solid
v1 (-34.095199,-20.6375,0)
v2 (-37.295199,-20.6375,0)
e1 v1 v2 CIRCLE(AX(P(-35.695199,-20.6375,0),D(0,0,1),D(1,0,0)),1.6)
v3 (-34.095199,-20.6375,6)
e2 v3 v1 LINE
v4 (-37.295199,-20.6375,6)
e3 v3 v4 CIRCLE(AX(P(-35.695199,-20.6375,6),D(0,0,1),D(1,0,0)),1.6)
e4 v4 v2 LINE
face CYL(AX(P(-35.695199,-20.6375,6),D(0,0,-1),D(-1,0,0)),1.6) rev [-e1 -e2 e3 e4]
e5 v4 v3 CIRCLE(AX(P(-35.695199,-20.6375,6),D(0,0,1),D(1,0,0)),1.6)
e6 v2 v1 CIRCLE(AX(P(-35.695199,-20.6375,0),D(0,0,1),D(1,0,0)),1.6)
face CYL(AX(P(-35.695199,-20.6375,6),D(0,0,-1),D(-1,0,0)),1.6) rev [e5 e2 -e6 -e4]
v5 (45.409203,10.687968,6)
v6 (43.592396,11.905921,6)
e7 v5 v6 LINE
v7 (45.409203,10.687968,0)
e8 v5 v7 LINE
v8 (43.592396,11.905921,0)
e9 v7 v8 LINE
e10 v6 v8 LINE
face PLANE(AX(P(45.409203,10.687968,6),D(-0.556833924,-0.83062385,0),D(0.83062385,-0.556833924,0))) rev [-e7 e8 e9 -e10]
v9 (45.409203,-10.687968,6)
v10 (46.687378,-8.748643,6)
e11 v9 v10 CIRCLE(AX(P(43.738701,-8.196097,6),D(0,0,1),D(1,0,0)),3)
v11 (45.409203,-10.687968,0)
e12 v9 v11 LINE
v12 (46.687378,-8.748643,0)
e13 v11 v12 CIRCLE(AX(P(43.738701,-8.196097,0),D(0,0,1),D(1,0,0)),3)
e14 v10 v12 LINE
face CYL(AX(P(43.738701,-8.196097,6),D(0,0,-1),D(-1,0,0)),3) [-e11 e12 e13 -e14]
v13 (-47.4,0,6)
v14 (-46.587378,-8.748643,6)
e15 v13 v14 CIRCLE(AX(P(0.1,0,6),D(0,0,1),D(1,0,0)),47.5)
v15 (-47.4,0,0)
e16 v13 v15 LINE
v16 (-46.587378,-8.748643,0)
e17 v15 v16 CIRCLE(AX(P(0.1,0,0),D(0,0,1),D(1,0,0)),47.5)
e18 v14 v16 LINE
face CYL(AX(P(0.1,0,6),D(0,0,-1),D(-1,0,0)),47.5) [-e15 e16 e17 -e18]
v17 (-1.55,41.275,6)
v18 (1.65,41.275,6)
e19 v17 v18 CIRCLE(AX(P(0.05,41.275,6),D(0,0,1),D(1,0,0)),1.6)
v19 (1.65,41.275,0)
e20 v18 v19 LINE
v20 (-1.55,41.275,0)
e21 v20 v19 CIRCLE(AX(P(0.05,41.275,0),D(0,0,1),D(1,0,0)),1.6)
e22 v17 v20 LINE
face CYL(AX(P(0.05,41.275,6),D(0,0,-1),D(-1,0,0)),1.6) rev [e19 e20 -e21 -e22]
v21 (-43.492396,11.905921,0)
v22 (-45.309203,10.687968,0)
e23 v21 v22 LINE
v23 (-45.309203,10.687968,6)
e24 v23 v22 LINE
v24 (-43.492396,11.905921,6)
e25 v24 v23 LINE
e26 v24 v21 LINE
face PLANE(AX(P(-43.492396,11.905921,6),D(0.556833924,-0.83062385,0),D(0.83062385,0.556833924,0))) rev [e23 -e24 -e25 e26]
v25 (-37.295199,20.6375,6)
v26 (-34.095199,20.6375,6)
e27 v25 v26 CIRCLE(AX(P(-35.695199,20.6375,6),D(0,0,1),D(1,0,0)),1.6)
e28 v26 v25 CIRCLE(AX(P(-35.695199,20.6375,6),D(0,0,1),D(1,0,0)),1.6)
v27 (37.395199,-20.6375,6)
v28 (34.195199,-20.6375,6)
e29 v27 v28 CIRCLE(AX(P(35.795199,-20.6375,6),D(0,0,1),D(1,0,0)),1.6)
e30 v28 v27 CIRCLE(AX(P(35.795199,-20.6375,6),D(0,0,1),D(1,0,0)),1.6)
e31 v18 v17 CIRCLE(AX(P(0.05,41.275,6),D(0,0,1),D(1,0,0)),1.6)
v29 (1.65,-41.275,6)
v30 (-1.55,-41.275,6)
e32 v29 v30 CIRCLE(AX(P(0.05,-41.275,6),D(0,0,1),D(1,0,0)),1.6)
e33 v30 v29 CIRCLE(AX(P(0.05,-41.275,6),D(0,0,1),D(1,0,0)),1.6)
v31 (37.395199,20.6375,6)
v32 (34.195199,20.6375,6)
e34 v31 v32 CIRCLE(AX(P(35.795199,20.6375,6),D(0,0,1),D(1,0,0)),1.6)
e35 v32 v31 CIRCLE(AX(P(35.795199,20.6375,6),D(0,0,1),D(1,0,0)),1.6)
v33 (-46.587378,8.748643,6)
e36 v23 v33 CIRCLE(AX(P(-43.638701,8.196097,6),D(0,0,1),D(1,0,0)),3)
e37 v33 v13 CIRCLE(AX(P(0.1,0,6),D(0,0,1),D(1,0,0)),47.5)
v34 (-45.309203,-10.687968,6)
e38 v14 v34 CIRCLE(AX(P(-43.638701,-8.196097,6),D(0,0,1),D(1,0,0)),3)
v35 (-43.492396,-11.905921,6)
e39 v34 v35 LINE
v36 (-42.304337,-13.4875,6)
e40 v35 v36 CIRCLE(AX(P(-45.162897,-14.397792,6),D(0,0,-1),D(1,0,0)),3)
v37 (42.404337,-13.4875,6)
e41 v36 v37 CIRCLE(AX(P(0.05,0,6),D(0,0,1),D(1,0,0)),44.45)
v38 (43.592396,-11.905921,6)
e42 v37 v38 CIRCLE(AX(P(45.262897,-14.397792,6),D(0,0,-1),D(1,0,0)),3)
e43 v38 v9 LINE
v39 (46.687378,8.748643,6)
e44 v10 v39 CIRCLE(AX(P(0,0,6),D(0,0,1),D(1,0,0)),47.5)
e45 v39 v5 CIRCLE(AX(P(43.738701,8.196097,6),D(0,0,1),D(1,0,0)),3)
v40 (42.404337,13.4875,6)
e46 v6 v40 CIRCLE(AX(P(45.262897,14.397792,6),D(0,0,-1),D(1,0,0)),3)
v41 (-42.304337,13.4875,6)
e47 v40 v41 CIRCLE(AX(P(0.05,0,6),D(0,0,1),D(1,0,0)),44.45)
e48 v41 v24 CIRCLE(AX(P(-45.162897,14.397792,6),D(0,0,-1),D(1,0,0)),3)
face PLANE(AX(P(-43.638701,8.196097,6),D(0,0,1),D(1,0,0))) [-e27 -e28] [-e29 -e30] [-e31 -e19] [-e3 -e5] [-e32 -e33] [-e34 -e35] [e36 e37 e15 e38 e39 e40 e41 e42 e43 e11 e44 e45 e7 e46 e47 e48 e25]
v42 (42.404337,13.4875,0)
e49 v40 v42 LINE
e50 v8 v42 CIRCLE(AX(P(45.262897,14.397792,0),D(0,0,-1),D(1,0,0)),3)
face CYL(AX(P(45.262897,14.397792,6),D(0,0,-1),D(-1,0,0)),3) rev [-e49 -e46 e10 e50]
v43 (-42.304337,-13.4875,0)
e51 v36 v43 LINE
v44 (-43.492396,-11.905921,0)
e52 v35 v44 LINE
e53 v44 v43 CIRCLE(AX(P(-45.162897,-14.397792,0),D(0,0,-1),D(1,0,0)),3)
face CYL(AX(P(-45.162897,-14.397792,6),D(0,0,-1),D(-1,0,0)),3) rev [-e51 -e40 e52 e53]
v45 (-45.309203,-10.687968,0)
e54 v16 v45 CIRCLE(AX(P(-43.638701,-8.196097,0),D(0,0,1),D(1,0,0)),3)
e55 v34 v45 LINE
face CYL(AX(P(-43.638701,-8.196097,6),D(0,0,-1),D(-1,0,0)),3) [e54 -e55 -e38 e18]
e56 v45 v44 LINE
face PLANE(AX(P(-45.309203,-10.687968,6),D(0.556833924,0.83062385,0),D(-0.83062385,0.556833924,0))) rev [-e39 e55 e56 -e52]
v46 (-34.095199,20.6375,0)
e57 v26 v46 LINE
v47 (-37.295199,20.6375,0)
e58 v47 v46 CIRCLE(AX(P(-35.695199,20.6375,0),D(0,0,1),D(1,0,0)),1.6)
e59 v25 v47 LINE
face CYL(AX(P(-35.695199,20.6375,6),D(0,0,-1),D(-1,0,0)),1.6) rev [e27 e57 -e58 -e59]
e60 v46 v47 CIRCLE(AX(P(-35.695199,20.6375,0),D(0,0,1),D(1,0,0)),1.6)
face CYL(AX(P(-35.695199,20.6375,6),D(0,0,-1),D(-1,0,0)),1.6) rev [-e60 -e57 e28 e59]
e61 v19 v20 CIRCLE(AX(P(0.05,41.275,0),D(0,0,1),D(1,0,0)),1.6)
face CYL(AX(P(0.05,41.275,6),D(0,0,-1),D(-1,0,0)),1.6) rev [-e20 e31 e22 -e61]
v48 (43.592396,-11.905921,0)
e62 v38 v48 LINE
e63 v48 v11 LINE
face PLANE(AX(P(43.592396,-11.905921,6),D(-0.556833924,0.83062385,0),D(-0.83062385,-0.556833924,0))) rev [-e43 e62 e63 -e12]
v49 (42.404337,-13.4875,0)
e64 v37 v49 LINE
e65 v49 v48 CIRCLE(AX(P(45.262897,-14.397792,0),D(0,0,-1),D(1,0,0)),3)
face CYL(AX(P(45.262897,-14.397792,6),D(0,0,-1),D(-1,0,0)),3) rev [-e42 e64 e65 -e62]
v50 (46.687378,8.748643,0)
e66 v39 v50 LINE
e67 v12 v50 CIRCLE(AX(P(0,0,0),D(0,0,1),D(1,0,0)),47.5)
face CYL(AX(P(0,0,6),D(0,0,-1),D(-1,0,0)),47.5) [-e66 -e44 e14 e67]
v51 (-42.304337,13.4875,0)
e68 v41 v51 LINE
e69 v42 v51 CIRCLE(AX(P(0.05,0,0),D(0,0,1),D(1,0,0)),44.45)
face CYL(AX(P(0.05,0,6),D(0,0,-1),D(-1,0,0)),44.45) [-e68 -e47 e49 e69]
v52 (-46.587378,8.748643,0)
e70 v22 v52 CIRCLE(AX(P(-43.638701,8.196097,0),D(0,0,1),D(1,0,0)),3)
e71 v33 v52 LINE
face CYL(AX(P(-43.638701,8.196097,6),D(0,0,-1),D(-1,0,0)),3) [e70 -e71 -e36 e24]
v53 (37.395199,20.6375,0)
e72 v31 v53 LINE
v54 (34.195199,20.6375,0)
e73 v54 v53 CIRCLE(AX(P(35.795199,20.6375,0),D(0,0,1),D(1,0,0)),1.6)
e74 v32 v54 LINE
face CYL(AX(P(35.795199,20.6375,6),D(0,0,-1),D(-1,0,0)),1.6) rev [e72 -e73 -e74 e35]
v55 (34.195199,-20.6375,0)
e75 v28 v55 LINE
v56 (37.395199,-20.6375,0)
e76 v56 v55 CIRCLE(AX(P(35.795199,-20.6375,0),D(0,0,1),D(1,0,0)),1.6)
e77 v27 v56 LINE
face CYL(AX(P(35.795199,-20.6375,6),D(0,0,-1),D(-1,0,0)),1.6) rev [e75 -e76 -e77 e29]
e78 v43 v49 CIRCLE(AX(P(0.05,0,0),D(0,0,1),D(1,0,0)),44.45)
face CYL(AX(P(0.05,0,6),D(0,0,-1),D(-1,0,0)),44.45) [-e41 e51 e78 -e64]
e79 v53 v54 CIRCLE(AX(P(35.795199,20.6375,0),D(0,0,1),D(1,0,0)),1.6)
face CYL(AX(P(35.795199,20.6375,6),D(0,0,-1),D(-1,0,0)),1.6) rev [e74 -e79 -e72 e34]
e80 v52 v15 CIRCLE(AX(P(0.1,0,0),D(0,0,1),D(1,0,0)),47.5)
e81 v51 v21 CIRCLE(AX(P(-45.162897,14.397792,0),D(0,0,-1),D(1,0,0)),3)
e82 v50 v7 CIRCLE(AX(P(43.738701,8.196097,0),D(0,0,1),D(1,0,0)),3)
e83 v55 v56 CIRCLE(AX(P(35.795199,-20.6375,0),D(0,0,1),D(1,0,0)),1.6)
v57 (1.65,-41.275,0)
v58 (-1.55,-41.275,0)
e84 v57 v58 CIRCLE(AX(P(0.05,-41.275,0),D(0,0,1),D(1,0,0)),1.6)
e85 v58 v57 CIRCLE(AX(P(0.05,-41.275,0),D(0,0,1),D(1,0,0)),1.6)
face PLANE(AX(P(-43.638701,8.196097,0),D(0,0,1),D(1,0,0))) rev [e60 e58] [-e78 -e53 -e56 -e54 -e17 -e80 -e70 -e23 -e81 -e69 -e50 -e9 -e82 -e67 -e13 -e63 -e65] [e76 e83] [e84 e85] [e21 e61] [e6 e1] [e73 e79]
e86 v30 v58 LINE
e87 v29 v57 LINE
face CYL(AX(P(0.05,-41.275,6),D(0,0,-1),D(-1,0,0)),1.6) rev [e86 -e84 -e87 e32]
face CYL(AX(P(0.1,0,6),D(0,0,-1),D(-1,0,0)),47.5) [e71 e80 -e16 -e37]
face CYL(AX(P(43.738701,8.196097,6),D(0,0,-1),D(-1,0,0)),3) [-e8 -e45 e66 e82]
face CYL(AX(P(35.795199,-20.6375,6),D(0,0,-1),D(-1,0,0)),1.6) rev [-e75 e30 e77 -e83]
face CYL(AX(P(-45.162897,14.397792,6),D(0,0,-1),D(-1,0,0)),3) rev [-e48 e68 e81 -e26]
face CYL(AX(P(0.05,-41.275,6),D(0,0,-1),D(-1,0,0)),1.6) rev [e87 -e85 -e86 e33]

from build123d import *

# Parameters (mm, degrees)
SKETCH1_R           = 1.6
BOSS_EXTRUDE1_DEPTH = 6


with BuildPart() as part:
    # Sketch1 → Boss-Extrude1 (new body)
    with BuildSketch(Plane.XY):
        with BuildLine():
            Line((-45.309203126, -10.68796842), (-43.492395524, -11.905920573))
            ThreePointArc((-43.492395524, -11.905920573), (-42.764262434, -12.595973377), (-42.304336877, -13.487499682))
            ThreePointArc((-42.304336877, -13.487499682), (0.05, -44.45), (42.404336877, -13.487499682))
            ThreePointArc((42.404336877, -13.487499682), (42.864262434, -12.595973377), (43.592395524, -11.905920573))
            Line((43.592395524, -11.905920573), (45.409203126, -10.68796842))
            ThreePointArc((45.409203126, -10.68796842), (46.243586183, -9.847021456), (46.68737785, -8.748642725))
            ThreePointArc((46.68737785, -8.748642725), (47.5, 0), (46.68737785, 8.748642725))
            ThreePointArc((46.68737785, 8.748642725), (46.243586183, 9.847021456), (45.409203126, 10.68796842))
            Line((45.409203126, 10.68796842), (43.592395524, 11.905920573))
            ThreePointArc((43.592395524, 11.905920573), (42.864262434, 12.595973377), (42.404336877, 13.487499682))
            ThreePointArc((42.404336877, 13.487499682), (0.05, 44.45), (-42.304336877, 13.487499682))
            ThreePointArc((-42.304336877, 13.487499682), (-42.764262434, 12.595973377), (-43.492395524, 11.905920573))
            Line((-43.492395524, 11.905920573), (-45.309203126, 10.68796842))
            ThreePointArc((-45.309203126, 10.68796842), (-46.143586183, 9.847021456), (-46.58737785, 8.748642725))
            ThreePointArc((-46.58737785, 8.748642725), (-47.4, 0), (-46.58737785, -8.748642725))
            ThreePointArc((-46.58737785, -8.748642725), (-46.143586183, -9.847021456), (-45.309203126, -10.68796842))
        make_face()
        with Locations((-35.695198541, 20.6375)):
            Circle(SKETCH1_R, mode=Mode.SUBTRACT)
        with Locations((-35.695198541, -20.6375)):
            Circle(SKETCH1_R, mode=Mode.SUBTRACT)
        with Locations((35.795198541, -20.6375)):
            Circle(SKETCH1_R, mode=Mode.SUBTRACT)
        with Locations((35.795198541, 20.6375)):
            Circle(SKETCH1_R, mode=Mode.SUBTRACT)
        with Locations((0.05, -41.275)):
            Circle(SKETCH1_R, mode=Mode.SUBTRACT)
        with Locations((0.05, 41.275)):
            Circle(SKETCH1_R, mode=Mode.SUBTRACT)
    extrude(amount=BOSS_EXTRUDE1_DEPTH)


solid = part.part
